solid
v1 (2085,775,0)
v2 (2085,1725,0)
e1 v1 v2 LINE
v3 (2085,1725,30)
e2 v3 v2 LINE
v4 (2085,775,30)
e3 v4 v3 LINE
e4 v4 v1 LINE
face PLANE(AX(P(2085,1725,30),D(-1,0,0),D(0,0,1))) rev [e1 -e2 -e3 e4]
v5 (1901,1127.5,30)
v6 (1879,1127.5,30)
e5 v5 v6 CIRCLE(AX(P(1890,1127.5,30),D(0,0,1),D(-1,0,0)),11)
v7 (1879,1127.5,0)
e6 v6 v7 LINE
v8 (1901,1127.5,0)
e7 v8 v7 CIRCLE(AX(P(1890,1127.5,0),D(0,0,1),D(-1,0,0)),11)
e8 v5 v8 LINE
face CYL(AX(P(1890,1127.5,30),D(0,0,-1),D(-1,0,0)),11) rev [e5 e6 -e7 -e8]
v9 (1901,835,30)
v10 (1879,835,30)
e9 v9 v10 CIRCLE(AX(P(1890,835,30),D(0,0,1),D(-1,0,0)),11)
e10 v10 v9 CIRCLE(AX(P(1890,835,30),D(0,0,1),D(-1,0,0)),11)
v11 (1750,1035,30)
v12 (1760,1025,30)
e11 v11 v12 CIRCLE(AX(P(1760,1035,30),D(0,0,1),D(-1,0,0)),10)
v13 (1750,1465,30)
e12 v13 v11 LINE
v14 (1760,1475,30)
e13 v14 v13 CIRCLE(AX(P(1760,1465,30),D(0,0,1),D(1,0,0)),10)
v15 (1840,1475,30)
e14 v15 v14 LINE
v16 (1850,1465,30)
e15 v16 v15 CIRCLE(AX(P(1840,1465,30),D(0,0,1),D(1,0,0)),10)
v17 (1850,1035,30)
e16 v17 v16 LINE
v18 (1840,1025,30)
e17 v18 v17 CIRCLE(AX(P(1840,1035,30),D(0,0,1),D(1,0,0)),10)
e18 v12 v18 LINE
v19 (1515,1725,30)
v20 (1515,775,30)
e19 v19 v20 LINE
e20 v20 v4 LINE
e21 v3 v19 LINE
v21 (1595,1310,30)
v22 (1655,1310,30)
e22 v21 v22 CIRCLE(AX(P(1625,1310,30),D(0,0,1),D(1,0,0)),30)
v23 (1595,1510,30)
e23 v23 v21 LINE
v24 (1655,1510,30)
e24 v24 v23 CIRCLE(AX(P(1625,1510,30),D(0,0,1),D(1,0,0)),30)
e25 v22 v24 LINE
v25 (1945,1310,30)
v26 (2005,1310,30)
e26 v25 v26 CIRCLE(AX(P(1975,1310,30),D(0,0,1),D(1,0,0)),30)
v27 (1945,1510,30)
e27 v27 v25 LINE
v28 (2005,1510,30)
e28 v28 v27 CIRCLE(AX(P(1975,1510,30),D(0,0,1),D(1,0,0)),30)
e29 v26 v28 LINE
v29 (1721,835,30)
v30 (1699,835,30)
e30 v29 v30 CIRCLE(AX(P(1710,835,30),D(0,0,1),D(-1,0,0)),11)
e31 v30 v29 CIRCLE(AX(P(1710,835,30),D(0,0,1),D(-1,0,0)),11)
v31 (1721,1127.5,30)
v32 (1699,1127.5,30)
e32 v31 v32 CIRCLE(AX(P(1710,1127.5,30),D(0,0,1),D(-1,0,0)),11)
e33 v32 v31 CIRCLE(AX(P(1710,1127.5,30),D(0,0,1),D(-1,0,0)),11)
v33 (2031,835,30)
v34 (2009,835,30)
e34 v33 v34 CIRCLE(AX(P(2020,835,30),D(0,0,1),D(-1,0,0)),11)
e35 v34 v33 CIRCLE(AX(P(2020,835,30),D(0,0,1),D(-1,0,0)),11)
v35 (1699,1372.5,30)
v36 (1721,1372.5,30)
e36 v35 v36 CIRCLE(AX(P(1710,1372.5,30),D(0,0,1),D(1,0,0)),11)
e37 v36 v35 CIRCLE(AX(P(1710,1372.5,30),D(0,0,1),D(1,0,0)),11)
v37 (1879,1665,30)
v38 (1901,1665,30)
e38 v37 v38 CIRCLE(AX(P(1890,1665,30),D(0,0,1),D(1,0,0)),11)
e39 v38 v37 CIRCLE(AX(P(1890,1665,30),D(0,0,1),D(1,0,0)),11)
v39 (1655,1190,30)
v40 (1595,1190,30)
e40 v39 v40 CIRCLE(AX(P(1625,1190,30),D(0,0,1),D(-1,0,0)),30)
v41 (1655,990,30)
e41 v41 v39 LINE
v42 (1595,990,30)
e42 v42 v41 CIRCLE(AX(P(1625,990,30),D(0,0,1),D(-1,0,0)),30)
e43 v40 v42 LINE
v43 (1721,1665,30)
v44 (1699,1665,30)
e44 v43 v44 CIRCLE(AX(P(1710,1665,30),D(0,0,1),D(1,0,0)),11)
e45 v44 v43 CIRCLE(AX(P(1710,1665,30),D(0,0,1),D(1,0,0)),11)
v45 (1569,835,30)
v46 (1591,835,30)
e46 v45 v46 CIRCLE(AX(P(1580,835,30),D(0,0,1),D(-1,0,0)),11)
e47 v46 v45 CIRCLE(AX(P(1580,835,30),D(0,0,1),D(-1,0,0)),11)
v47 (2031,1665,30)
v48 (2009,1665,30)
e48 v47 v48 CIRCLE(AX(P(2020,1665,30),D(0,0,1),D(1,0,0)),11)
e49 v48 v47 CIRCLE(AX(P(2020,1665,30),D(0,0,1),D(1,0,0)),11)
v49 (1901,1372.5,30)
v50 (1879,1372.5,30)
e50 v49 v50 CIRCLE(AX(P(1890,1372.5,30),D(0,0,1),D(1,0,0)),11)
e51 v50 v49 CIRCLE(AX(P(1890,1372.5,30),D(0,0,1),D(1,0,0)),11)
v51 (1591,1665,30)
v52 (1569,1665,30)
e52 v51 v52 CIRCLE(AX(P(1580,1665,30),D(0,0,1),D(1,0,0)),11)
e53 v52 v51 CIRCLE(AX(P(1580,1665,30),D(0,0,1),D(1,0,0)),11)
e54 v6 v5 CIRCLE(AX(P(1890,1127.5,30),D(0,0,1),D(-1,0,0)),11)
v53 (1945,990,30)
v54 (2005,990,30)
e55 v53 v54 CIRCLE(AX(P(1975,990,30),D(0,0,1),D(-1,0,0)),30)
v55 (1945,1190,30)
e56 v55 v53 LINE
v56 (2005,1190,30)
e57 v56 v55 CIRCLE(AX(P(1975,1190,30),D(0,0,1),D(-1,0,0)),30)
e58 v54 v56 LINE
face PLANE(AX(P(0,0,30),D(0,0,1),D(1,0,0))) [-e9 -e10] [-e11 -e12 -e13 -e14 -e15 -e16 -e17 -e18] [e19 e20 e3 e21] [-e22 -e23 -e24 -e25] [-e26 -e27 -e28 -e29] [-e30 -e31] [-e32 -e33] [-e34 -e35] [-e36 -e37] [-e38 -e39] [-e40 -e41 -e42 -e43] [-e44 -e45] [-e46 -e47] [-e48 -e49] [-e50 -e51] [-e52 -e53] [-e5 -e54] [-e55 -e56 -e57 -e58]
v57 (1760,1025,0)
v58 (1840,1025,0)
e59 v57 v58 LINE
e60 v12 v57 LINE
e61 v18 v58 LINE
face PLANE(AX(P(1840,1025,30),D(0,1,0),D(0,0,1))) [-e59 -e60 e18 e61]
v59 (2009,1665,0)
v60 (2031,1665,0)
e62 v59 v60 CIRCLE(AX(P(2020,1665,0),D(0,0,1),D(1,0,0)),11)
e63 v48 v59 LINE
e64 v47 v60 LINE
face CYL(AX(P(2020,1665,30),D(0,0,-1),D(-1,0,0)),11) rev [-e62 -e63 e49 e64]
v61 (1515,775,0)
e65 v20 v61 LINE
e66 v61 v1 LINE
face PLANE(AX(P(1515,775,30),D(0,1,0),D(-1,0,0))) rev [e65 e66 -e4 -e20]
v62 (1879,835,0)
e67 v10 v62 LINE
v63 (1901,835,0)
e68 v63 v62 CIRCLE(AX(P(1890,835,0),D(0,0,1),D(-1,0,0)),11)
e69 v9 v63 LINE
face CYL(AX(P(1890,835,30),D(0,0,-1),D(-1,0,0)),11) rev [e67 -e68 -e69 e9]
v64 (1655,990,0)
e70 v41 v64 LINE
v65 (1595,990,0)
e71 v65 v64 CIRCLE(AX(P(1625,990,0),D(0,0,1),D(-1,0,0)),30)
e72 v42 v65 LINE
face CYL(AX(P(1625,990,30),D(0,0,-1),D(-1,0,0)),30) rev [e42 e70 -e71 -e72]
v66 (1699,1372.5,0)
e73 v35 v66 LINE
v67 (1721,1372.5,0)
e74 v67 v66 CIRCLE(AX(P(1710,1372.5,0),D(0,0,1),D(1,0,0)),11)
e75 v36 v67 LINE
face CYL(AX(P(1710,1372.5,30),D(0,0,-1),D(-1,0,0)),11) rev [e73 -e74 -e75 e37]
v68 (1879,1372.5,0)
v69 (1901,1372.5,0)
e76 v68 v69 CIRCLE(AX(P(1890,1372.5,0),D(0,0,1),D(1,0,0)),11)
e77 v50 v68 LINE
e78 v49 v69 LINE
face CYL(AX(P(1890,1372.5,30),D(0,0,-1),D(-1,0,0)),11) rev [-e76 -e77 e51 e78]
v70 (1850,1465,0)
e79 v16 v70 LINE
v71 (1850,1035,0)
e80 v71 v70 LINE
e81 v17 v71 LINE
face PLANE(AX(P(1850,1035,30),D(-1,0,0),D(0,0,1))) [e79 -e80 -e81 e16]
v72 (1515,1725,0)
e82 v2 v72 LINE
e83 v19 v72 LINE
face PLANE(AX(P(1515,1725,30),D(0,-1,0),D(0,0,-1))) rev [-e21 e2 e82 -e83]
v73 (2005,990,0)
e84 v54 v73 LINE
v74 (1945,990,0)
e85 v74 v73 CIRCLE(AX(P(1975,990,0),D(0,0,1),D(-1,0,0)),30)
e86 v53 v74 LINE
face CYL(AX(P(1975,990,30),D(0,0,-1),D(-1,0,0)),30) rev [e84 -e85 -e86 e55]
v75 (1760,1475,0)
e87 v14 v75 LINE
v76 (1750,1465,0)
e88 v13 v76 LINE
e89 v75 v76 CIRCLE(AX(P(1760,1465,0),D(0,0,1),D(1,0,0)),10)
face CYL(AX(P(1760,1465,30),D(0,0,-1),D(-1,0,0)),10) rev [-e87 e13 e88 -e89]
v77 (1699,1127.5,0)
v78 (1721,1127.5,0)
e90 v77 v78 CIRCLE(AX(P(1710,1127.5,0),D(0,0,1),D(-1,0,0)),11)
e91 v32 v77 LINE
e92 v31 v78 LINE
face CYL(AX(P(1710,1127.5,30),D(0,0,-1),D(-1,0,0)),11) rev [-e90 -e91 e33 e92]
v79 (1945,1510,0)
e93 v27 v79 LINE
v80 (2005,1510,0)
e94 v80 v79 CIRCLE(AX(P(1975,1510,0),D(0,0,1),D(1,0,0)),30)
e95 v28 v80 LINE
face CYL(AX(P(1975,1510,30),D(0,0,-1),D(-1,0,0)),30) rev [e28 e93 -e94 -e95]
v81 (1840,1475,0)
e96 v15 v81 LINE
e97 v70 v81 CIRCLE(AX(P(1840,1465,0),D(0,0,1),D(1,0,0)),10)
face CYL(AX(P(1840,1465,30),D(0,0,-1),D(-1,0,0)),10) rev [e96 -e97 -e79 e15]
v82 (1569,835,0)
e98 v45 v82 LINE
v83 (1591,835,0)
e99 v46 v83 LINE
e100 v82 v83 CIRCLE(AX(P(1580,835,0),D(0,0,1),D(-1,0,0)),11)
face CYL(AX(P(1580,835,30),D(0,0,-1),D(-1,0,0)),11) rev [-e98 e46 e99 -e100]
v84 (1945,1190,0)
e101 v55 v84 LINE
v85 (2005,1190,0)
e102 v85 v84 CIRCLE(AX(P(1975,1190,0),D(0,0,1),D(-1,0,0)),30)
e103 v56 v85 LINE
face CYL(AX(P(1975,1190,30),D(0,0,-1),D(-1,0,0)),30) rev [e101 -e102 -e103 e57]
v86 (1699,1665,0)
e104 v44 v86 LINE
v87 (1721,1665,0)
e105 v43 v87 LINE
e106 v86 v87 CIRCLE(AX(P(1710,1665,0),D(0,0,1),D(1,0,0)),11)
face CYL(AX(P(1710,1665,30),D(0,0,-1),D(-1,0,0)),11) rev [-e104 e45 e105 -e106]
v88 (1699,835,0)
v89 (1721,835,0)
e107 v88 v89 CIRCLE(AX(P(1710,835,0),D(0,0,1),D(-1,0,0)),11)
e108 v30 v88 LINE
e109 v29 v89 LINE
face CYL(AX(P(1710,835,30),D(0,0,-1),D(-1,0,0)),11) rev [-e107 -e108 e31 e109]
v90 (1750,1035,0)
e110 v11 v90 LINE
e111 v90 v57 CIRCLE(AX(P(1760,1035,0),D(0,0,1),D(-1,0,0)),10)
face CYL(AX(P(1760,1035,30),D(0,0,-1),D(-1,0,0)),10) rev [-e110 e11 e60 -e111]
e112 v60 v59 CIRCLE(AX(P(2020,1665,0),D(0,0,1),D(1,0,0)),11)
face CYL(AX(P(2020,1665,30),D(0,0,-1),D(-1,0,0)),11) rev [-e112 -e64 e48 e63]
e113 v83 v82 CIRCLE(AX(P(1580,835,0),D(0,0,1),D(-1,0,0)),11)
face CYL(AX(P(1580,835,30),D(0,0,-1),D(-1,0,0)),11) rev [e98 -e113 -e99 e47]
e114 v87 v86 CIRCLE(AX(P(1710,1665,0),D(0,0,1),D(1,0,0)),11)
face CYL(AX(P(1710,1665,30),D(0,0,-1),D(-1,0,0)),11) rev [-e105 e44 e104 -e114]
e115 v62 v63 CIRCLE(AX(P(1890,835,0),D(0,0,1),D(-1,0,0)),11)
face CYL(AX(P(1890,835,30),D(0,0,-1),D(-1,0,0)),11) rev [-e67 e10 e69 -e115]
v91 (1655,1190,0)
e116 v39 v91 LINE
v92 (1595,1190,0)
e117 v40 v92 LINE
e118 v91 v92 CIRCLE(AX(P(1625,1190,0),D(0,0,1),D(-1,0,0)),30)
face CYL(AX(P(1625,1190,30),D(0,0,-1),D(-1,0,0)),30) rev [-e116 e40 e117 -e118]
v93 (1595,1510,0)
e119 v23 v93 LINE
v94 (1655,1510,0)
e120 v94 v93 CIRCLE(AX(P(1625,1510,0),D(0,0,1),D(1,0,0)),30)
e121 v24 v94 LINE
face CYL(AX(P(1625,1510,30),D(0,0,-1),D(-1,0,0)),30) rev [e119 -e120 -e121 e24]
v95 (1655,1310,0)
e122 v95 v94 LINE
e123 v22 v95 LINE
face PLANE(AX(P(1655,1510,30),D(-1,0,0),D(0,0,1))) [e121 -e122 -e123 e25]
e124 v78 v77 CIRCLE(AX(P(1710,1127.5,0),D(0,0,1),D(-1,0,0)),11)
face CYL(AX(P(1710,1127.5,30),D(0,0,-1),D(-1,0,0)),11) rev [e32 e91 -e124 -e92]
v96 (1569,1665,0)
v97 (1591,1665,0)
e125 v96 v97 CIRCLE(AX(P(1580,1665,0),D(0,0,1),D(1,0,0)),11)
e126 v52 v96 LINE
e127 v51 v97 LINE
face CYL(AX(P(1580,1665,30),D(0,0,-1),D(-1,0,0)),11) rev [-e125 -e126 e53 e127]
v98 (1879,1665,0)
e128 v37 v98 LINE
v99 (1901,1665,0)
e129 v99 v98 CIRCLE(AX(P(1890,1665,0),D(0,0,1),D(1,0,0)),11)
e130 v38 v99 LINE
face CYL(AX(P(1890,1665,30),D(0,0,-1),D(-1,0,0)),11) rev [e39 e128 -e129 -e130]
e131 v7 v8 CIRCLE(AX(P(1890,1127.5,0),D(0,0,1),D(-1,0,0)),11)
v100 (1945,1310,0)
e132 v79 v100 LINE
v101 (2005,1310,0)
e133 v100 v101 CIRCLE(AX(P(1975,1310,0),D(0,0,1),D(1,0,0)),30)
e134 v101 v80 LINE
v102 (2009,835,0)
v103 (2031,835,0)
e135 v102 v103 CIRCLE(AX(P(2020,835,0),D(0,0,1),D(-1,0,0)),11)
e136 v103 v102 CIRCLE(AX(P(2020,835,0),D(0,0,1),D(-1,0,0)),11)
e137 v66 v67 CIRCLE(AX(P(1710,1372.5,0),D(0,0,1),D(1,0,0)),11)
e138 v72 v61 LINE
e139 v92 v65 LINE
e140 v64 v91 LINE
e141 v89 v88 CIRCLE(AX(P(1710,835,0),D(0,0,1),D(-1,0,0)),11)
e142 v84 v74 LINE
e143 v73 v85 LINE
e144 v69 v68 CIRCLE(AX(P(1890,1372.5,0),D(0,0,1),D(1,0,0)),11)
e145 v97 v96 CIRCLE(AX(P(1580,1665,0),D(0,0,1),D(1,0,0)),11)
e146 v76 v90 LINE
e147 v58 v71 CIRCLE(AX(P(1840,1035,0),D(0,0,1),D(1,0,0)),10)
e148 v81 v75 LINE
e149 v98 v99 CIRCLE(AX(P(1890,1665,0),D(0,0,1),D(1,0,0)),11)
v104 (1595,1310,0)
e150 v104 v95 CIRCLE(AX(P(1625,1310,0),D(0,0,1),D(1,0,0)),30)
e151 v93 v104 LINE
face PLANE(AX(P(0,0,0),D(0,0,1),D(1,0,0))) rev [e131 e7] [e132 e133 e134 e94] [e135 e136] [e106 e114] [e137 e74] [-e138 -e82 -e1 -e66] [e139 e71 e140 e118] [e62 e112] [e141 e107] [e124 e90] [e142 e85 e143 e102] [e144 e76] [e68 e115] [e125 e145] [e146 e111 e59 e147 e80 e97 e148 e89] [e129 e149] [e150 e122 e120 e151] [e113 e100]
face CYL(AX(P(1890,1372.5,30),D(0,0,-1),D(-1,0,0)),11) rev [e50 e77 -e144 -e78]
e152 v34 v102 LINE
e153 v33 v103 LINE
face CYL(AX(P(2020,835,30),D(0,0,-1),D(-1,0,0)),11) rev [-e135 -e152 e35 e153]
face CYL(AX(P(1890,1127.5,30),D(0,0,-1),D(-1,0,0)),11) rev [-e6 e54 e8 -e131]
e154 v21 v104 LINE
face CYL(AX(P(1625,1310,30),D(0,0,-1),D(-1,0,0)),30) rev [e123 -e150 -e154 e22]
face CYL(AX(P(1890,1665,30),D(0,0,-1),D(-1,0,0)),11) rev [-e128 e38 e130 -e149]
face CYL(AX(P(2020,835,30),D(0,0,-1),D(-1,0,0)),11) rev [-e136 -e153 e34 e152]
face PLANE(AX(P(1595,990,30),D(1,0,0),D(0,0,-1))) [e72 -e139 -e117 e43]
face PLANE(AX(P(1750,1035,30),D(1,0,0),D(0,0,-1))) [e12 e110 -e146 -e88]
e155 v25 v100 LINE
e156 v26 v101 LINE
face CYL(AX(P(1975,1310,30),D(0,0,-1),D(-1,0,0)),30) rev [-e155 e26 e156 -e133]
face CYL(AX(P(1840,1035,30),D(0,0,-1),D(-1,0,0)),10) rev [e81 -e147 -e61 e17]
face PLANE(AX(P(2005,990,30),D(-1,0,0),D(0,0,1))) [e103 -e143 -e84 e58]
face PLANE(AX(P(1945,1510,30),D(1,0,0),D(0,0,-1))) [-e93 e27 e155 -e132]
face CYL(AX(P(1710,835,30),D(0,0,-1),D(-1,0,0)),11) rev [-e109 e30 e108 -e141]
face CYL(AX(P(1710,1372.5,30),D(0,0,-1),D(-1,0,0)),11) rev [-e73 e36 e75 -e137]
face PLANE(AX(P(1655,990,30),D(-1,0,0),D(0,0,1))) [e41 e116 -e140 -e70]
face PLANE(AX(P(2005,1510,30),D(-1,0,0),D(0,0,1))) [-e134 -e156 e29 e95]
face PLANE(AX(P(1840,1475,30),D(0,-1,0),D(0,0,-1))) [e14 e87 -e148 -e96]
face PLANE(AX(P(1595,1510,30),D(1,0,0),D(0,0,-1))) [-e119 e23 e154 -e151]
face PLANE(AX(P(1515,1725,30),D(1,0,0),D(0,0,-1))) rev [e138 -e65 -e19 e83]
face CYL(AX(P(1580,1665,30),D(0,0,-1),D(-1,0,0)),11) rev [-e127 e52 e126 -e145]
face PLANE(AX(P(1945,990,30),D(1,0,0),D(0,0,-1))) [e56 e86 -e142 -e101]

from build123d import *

# Parameters (mm, degrees)
SKETCH_1_W      = 570
SKETCH_1_H      = 950
SKETCH_1_R      = 11
EXTRUDE_1_DEPTH = 30


with BuildPart() as part:
    # 草图1 → 凸台-拉伸1 (new body)
    with BuildSketch(Plane.XY):
        with Locations((1800, 1250)):
            Rectangle(SKETCH_1_W, SKETCH_1_H)
        with Locations((1580, 1665)):
            Circle(SKETCH_1_R, mode=Mode.SUBTRACT)
        with Locations((1710, 1665)):
            Circle(SKETCH_1_R, mode=Mode.SUBTRACT)
        with Locations((1890, 1665)):
            Circle(SKETCH_1_R, mode=Mode.SUBTRACT)
        with Locations((2020, 1665)):
            Circle(SKETCH_1_R, mode=Mode.SUBTRACT)
        with Locations((1710, 1372.5)):
            Circle(SKETCH_1_R, mode=Mode.SUBTRACT)
        with Locations((1890, 1372.5)):
            Circle(SKETCH_1_R, mode=Mode.SUBTRACT)
        with Locations(Location((1710, 1127.5, 0), (0, 0, 180))):
            Circle(SKETCH_1_R, mode=Mode.SUBTRACT)
        with Locations(Location((1890, 1127.5, 0), (0, 0, 180))):
            Circle(SKETCH_1_R, mode=Mode.SUBTRACT)
        with Locations(Location((2020, 835, 0), (0, 0, 180))):
            Circle(SKETCH_1_R, mode=Mode.SUBTRACT)
        with Locations(Location((1890, 835, 0), (0, 0, 180))):
            Circle(SKETCH_1_R, mode=Mode.SUBTRACT)
        with Locations(Location((1710, 835, 0), (0, 0, 180))):
            Circle(SKETCH_1_R, mode=Mode.SUBTRACT)
        with Locations(Location((1580, 835, 0), (0, 0, 180))):
            Circle(SKETCH_1_R, mode=Mode.SUBTRACT)
        with BuildLine():
            Line((1840, 1025), (1760, 1025))
            ThreePointArc((1760, 1025), (1752.928932188, 1027.928932188), (1750, 1035))
            Line((1750, 1035), (1750, 1465))
            ThreePointArc((1750, 1465), (1752.928932188, 1472.071067812), (1760, 1475))
            Line((1760, 1475), (1840, 1475))
            ThreePointArc((1840, 1475), (1847.071067812, 1472.071067812), (1850, 1465))
            Line((1850, 1465), (1850, 1035))
            ThreePointArc((1850, 1035), (1847.071067812, 1027.928932188), (1840, 1025))
        make_face(mode=Mode.SUBTRACT)
        with BuildLine():
            Line((1655, 1510), (1655, 1310))
            ThreePointArc((1655, 1310), (1625, 1280), (1595, 1310))
            Line((1595, 1310), (1595, 1510))
            ThreePointArc((1595, 1510), (1625, 1540), (1655, 1510))
        make_face(mode=Mode.SUBTRACT)
        with BuildLine():
            Line((2005, 1510), (2005, 1310))
            ThreePointArc((2005, 1310), (1975, 1280), (1945, 1310))
            Line((1945, 1310), (1945, 1510))
            ThreePointArc((1945, 1510), (1975, 1540), (2005, 1510))
        make_face(mode=Mode.SUBTRACT)
        with BuildLine():
            Line((2005, 990), (2005, 1190))
            ThreePointArc((2005, 1190), (1975, 1220), (1945, 1190))
            Line((1945, 1190), (1945, 990))
            ThreePointArc((1945, 990), (1975, 960), (2005, 990))
        make_face(mode=Mode.SUBTRACT)
        with BuildLine():
            Line((1655, 990), (1655, 1190))
            ThreePointArc((1655, 1190), (1625, 1220), (1595, 1190))
            Line((1595, 1190), (1595, 990))
            ThreePointArc((1595, 990), (1625, 960), (1655, 990))
        make_face(mode=Mode.SUBTRACT)
    extrude(amount=EXTRUDE_1_DEPTH)


solid = part.part
